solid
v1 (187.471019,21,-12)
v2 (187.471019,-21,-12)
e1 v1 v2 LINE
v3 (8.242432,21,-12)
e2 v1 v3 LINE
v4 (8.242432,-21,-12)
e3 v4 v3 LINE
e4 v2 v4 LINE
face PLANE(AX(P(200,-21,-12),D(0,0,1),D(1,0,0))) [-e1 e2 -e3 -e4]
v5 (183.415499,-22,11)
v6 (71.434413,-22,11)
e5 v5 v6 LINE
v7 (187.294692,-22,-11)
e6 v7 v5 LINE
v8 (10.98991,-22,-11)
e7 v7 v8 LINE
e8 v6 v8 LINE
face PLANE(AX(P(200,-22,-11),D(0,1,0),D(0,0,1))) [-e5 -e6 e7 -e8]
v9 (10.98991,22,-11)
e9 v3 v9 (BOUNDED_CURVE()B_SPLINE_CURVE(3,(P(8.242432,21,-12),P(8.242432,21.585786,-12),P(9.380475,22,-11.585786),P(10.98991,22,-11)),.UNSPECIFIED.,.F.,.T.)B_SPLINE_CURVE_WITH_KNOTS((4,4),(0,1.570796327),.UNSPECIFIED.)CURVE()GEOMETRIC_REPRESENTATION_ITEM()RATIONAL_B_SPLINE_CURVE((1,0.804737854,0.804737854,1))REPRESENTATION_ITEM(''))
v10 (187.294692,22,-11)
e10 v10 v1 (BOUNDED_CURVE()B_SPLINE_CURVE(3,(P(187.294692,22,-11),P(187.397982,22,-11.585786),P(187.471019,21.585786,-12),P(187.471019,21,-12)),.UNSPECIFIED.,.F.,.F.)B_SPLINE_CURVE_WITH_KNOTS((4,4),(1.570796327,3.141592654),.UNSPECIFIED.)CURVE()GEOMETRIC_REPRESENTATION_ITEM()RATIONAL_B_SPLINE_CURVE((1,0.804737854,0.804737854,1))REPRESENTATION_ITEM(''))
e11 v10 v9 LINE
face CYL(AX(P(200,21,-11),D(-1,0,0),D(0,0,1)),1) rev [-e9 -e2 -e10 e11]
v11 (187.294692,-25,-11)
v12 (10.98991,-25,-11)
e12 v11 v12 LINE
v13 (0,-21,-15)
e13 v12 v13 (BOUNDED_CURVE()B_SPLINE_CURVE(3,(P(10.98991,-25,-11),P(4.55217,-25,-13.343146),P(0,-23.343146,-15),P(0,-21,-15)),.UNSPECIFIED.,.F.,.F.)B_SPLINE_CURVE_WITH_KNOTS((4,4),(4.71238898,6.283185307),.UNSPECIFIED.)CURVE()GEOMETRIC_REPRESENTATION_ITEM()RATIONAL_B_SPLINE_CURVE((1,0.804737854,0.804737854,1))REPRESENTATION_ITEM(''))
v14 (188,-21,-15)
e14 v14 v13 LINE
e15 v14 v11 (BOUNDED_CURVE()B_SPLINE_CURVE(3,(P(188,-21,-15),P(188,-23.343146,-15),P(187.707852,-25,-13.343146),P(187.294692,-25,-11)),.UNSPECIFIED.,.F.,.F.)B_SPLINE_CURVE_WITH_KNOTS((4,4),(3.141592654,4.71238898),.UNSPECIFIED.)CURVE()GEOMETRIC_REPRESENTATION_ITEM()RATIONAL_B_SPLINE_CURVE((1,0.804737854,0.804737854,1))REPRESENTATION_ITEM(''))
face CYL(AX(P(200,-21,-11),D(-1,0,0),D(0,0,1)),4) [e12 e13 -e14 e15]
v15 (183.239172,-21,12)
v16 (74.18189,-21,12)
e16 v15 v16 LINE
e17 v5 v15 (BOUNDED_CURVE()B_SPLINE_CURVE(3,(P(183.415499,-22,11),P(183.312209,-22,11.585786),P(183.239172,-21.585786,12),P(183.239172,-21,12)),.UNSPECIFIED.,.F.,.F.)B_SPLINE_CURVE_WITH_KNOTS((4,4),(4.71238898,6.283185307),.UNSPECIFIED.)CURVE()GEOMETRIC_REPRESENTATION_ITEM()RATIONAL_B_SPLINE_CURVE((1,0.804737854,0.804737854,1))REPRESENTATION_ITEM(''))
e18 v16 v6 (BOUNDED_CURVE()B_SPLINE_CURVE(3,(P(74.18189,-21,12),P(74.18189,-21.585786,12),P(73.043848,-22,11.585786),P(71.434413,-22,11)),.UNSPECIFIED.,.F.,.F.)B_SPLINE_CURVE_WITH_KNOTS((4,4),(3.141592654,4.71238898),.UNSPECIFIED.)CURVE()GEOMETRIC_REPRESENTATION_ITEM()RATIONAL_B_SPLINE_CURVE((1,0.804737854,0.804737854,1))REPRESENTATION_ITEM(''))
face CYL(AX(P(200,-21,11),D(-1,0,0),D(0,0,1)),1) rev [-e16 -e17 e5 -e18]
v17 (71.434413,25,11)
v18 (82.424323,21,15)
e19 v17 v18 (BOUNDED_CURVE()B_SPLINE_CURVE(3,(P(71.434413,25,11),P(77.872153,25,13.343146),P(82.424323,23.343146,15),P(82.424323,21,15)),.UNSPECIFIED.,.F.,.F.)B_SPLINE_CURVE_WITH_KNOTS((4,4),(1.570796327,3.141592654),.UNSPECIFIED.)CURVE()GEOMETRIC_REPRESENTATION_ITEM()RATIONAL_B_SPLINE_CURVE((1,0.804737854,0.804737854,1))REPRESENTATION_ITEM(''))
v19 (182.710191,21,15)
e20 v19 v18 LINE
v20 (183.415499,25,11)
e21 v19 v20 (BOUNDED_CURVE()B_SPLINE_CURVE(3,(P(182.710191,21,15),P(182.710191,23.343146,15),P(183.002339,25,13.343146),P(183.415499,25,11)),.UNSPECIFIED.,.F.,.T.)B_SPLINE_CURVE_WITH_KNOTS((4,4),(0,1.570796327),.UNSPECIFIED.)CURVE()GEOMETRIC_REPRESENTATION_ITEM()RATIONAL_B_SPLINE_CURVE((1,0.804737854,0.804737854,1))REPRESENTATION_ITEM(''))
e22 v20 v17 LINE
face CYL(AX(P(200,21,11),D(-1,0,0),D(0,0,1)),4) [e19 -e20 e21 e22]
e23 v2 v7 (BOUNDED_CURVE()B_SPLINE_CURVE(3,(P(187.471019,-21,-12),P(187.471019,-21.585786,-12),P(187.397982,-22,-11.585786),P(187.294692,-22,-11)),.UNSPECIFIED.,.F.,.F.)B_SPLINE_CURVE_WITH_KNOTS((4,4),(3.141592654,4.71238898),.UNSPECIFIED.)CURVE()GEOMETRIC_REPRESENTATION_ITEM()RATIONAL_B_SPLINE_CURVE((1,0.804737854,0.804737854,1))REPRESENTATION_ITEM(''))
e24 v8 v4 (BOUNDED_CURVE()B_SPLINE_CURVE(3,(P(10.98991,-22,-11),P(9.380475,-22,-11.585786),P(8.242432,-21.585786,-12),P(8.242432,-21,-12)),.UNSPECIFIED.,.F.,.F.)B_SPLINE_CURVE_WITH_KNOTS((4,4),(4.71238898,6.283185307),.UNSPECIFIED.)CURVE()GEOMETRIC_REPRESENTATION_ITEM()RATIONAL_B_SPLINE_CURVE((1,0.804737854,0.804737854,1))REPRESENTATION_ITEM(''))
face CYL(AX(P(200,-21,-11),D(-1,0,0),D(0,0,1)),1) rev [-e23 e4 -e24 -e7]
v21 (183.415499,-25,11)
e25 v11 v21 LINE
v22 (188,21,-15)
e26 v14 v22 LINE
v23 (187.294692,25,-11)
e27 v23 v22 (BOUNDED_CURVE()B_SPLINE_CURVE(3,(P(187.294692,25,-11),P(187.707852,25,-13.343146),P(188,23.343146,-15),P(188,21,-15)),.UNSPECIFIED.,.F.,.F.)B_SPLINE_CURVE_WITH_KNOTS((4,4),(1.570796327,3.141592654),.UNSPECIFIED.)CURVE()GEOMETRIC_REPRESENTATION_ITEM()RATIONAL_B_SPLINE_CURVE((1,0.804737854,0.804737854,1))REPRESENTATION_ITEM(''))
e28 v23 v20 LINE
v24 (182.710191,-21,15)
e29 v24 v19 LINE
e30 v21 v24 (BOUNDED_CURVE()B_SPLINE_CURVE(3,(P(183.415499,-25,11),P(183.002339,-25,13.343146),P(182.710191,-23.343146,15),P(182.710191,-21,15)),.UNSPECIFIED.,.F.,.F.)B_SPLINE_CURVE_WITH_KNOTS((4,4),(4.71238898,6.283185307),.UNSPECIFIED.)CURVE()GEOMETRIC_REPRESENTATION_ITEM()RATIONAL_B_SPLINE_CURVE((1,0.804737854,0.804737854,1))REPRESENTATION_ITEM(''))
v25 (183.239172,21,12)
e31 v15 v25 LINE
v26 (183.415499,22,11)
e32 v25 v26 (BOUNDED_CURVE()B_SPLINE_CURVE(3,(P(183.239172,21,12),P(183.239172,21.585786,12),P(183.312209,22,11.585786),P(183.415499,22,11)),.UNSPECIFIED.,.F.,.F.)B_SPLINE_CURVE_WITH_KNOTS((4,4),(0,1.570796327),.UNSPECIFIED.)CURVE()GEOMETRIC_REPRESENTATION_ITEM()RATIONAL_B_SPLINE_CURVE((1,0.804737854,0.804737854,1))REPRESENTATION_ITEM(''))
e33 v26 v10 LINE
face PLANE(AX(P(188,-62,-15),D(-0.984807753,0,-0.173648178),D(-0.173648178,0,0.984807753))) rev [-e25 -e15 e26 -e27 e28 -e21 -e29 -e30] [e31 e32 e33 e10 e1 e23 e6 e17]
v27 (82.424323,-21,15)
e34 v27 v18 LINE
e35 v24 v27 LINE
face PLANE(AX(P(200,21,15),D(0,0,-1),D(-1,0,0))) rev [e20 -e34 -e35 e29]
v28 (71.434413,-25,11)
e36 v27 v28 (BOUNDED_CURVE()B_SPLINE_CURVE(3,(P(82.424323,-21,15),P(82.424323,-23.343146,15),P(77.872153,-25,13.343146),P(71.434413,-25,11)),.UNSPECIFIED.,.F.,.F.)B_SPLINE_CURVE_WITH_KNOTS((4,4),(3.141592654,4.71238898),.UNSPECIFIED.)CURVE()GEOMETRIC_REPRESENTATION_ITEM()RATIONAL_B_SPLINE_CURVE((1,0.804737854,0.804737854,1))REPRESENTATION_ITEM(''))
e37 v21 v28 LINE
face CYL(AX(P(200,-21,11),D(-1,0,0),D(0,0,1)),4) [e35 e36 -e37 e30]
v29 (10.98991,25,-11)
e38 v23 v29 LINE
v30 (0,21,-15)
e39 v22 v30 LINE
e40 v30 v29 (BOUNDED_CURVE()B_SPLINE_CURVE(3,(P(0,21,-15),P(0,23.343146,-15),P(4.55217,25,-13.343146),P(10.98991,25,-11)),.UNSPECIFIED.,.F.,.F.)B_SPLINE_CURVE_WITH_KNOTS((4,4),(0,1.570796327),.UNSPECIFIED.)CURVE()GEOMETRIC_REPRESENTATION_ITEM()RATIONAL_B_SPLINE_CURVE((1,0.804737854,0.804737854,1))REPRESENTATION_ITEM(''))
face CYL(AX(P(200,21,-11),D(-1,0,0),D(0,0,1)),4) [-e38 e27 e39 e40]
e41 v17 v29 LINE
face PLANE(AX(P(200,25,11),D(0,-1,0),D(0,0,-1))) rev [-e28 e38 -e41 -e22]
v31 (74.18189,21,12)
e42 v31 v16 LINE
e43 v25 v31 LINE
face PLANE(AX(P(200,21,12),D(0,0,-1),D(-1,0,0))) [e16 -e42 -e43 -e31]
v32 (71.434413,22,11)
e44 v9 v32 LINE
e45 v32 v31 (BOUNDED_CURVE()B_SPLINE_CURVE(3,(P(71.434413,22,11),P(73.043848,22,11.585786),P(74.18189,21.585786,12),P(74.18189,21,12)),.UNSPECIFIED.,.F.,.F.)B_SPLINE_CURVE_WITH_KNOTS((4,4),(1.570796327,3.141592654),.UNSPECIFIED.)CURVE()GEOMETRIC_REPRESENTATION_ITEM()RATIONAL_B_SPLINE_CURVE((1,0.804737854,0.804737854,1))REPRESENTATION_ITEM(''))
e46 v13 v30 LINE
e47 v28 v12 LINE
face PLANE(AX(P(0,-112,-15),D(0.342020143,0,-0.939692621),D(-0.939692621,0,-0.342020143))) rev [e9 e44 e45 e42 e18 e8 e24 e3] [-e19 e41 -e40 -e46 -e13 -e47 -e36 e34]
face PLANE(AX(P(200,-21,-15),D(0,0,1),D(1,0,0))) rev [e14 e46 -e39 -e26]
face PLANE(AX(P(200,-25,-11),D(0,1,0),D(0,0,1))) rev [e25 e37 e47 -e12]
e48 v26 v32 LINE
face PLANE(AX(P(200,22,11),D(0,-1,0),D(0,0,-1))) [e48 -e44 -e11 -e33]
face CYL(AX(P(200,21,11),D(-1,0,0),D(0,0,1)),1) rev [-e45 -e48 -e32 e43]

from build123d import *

# Parameters (mm, degrees)
SQUARE_TUBE_30_X_30_X_2_6_1_DEPTH = 200
CUT_EXTRUDE1_DEPTH                = 87
CUT_EXTRUDE2_DEPTH                = 137


with BuildPart() as part:
    # Sketch1 → Square tube 30 X 30 X 2.6(1) (new body)
    with BuildSketch(Plane.YZ):
        with BuildLine():
            Line((-21, -15), (21, -15))
            ThreePointArc((21, -15), (23.828427125, -13.828427125), (25, -11))
            Line((25, -11), (25, 11))
            ThreePointArc((25, 11), (23.828427125, 13.828427125), (21, 15))
            Line((21, 15), (-21, 15))
            ThreePointArc((-21, 15), (-23.828427125, 13.828427125), (-25, 11))
            Line((-25, 11), (-25, -11))
            ThreePointArc((-25, -11), (-23.828427125, -13.828427125), (-21, -15))
        make_face()
        with BuildLine():
            Line((-21, -12), (21, -12))
            ThreePointArc((21, -12), (21.707106781, -11.707106781), (22, -11))
            Line((22, -11), (22, 11))
            ThreePointArc((22, 11), (21.707106781, 11.707106781), (21, 12))
            Line((21, 12), (-21, 12))
            ThreePointArc((-21, 12), (-21.707106781, 11.707106781), (-22, 11))
            Line((-22, 11), (-22, -11))
            ThreePointArc((-22, -11), (-21.707106781, -11.707106781), (-21, -12))
        make_face(mode=Mode.SUBTRACT)
    extrude(amount=SQUARE_TUBE_30_X_30_X_2_6_1_DEPTH)

    # Sketch3 → Cut-Extrude1 (cut)
    with BuildSketch(Plane(origin=(0, 25, 0), x_dir=(1, 0, 0), z_dir=(0, 1, 0))):
        Polygon((188, 15), (182.710190579, -15), (200, -15), (200, 15), align=None)
    extrude(amount=-CUT_EXTRUDE1_DEPTH, mode=Mode.SUBTRACT)

    # Sketch4 → Cut-Extrude2 (cut)
    with BuildSketch(Plane(origin=(0, 25, 0), x_dir=(1, 0, 0), z_dir=(0, 1, 0))):
        Polygon((0, 15), (82.424322584, -15), (0, -15), align=None)
    extrude(amount=-CUT_EXTRUDE2_DEPTH, mode=Mode.SUBTRACT)


solid = part.part
